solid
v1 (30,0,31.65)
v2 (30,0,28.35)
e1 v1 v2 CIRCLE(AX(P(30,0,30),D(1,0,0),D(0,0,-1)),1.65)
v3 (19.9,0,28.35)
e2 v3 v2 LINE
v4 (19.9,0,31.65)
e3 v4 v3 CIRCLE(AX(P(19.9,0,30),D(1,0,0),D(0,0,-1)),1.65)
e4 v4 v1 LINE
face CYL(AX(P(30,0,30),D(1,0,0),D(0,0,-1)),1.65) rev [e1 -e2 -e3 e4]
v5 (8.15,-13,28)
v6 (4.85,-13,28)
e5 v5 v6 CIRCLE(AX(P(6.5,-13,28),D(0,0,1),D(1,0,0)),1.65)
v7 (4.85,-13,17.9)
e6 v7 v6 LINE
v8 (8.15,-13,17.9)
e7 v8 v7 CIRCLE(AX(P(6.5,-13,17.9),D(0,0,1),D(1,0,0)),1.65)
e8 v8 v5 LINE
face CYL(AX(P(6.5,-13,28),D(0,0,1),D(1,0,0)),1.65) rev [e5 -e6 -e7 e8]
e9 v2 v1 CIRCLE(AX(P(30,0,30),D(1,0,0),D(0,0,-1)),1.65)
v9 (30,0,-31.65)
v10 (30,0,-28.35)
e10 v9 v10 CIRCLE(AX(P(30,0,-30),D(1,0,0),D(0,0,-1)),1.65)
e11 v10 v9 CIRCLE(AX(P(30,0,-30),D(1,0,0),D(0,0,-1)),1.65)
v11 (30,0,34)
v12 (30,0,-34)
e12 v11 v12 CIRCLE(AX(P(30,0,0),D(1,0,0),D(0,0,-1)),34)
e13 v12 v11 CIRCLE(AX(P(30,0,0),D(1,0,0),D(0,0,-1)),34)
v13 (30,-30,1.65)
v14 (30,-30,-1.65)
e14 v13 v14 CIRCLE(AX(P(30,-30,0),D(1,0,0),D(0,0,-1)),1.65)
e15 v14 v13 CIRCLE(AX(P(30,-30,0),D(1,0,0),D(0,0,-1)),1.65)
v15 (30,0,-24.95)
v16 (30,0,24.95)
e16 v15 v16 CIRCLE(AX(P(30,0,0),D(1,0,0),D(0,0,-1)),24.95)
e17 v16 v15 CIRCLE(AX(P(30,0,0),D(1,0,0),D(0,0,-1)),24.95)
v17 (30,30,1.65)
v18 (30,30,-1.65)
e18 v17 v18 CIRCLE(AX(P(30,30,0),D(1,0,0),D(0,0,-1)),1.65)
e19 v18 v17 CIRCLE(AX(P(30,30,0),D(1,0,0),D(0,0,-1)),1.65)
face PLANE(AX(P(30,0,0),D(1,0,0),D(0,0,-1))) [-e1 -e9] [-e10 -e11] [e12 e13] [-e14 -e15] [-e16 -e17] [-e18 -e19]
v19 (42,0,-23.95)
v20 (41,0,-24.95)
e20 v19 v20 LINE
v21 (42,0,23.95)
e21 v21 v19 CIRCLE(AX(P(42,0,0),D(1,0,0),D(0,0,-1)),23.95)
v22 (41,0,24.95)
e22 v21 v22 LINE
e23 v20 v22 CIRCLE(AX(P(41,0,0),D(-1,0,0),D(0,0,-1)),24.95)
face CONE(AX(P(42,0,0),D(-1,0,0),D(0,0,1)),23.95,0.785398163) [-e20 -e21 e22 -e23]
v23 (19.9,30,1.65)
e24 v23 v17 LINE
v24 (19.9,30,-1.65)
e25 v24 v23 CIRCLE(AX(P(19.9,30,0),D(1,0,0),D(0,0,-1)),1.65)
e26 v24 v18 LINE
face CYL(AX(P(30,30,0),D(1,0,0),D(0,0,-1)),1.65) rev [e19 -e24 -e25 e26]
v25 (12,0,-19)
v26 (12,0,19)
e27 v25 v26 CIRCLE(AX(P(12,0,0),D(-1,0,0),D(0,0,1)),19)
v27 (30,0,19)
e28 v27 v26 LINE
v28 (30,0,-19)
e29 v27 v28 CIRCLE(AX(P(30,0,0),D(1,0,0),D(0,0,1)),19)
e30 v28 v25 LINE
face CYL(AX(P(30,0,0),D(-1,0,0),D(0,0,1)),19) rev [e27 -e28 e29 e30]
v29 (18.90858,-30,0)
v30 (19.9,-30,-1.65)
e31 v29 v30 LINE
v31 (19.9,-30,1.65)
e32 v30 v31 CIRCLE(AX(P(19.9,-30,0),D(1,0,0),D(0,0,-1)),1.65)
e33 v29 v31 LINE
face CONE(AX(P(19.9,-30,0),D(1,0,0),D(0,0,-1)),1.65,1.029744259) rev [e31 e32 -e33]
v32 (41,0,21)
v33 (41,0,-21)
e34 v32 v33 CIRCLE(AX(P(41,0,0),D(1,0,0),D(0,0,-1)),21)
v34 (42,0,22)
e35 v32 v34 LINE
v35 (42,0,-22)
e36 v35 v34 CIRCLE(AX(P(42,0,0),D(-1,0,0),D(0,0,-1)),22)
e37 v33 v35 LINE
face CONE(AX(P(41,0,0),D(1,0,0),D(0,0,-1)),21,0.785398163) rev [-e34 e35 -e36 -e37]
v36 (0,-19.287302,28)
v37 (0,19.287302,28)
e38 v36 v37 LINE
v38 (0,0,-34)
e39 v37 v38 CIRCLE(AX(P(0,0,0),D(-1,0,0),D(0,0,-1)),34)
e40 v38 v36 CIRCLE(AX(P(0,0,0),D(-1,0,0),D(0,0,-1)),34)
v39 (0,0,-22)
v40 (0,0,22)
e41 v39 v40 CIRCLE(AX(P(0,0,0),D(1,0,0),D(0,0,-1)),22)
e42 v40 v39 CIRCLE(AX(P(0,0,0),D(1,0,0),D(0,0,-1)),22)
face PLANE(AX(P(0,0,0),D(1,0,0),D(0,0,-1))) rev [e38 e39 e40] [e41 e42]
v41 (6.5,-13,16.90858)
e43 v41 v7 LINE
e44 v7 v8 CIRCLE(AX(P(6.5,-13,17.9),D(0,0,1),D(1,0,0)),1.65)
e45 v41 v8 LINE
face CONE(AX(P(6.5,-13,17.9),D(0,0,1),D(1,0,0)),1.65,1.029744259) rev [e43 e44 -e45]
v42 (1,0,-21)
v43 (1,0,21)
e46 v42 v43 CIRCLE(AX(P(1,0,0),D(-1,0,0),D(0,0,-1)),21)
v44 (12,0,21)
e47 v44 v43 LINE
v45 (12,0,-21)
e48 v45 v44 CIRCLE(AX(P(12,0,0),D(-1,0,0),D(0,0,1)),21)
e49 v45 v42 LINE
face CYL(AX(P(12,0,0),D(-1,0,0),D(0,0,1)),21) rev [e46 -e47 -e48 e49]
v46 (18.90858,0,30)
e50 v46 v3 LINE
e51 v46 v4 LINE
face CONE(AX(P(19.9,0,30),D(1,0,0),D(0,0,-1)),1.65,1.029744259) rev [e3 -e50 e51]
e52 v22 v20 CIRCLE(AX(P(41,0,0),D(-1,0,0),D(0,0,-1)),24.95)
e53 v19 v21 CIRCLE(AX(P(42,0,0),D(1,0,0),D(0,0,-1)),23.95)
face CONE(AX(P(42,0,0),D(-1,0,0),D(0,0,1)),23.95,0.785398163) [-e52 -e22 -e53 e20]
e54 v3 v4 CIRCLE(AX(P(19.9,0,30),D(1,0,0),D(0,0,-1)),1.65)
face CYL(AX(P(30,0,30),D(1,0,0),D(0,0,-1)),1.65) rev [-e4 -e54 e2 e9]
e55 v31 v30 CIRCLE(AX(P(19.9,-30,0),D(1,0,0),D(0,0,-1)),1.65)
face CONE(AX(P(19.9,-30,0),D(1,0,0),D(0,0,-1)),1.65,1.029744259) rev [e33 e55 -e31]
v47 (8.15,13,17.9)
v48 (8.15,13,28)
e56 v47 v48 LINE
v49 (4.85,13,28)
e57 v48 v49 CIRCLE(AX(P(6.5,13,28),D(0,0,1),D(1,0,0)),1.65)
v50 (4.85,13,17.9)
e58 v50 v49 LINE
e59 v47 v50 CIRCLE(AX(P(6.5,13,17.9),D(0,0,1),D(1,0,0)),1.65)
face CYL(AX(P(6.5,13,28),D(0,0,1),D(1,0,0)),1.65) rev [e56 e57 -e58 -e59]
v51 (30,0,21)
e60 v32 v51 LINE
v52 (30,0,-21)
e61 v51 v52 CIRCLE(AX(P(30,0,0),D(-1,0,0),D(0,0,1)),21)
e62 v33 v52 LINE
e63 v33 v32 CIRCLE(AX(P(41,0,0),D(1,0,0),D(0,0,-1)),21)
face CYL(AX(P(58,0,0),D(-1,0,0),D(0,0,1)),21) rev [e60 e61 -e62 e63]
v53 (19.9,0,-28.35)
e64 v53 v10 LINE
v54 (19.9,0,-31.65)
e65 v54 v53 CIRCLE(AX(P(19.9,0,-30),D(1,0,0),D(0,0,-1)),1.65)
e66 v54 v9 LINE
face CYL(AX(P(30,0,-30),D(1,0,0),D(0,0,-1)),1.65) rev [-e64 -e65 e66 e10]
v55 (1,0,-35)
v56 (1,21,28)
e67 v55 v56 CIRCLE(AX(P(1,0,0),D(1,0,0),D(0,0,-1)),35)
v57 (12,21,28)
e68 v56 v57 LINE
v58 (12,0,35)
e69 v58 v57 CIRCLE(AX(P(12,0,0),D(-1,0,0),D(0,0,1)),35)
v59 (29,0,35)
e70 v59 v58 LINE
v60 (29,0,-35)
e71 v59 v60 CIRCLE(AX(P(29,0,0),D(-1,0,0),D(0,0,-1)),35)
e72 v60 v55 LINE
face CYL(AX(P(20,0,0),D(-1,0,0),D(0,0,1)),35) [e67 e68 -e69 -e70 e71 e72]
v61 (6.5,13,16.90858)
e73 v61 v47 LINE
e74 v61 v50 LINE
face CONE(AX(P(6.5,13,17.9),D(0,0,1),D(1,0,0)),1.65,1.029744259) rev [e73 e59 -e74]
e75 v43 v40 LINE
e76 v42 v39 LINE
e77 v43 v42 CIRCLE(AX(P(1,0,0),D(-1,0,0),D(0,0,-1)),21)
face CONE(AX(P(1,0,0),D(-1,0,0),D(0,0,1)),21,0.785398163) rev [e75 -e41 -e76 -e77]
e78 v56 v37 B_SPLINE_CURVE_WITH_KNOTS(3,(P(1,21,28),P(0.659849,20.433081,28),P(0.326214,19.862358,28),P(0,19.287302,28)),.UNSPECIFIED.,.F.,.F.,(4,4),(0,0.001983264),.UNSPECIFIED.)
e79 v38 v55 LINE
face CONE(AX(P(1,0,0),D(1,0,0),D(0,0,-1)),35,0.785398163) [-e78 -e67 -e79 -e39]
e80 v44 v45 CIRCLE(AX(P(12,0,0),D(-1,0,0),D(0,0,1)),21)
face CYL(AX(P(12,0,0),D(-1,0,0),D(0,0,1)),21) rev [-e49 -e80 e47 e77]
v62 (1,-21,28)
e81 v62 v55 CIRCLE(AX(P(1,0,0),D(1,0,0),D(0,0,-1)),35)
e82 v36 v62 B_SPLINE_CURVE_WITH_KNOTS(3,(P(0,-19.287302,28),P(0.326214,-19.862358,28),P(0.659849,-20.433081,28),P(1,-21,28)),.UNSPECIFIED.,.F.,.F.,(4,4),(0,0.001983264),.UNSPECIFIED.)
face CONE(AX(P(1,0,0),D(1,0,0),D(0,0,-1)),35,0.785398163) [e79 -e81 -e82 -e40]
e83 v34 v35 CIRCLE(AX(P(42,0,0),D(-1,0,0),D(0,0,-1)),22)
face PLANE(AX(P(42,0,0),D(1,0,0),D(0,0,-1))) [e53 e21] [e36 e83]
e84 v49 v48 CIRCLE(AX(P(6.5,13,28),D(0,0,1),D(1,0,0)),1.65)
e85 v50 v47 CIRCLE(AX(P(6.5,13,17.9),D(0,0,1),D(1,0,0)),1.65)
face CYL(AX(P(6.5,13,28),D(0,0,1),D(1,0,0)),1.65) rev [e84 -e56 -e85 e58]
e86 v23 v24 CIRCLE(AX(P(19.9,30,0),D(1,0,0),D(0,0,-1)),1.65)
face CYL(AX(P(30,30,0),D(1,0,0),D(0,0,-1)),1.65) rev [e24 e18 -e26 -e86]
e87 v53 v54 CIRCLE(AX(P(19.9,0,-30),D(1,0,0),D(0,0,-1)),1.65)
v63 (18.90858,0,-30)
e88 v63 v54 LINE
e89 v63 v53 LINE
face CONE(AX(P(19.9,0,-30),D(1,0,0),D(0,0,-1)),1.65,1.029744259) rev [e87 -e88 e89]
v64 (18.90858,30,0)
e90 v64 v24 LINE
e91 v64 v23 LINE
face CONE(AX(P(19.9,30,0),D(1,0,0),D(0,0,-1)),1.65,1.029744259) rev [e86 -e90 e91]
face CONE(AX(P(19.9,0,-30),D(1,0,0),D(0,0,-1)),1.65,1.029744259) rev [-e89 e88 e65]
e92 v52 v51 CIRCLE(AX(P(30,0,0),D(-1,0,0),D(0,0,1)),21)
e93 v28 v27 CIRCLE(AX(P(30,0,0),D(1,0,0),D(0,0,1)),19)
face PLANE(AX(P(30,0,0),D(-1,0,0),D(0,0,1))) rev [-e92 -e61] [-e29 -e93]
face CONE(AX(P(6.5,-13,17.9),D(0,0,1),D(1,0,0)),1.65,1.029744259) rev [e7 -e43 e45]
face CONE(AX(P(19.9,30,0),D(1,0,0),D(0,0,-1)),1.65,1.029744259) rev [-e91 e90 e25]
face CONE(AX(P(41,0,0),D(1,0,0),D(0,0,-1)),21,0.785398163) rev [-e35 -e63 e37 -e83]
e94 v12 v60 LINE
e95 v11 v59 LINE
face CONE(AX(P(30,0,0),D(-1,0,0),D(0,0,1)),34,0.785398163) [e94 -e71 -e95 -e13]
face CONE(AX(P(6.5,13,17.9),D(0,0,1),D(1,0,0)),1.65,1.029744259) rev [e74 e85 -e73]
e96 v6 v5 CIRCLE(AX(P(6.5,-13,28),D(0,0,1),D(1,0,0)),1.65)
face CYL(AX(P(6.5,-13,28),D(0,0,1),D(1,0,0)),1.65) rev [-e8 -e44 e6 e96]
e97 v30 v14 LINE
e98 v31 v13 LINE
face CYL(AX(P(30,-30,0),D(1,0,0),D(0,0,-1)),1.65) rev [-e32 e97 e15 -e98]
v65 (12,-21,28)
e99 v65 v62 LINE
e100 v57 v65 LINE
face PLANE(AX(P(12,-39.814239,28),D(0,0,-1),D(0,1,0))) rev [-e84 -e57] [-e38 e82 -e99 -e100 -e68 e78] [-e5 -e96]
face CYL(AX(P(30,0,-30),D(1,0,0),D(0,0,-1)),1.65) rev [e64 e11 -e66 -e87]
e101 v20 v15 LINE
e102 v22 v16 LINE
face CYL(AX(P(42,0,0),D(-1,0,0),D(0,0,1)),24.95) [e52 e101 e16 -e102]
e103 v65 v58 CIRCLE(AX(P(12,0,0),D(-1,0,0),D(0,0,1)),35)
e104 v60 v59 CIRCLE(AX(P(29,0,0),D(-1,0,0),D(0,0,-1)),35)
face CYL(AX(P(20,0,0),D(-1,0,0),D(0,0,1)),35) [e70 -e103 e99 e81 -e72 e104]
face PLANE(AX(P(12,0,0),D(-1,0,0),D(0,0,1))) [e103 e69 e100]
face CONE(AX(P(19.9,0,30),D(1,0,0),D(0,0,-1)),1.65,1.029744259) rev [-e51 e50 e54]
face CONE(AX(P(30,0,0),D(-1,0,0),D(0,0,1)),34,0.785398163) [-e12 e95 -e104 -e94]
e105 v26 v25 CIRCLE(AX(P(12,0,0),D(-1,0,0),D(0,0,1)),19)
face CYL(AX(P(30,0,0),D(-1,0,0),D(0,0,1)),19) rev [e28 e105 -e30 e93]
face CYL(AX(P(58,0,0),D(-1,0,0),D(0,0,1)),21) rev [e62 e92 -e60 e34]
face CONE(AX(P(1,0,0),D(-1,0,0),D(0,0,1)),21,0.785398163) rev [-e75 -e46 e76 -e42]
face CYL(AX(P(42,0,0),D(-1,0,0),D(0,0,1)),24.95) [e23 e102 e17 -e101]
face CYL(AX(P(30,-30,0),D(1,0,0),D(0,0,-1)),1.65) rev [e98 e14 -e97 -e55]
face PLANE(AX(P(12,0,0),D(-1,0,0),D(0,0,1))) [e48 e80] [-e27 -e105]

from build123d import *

# Parameters (mm, degrees)
SKETCH1_R             = 35
BOSS_EXTRUDE1_DEPTH   = 20
SKETCH2_R             = 35
BOSS_EXTRUDE2_DEPTH   = 10
SKETCH3_R             = 24.95
BOSS_EXTRUDE3_DEPTH   = 12
SKETCH4_R             = 21
CUT_EXTRUDE1_DEPTH    = 12
SKETCH5_R             = 19
CUT_EXTRUDE2_DEPTH    = 18
SKETCH6_R             = 21
CUT_EXTRUDE3_DEPTH    = 28
CIRPATTERN1_COUNT     = 4
SKETCH9_W             = 82.925750659
SKETCH9_H             = 79.628478102
CUT_EXTRUDE4_DEPTH    = 12
M4_TAPPED_HOLE3_D     = 3.3
M4_TAPPED_HOLE3_DEPTH = 10.1
M4_TAPPED_HOLE3_TIP   = 0.991420021
CHAMFER1_SIZE         = 1


with BuildPart() as part:
    # Sketch1 → Boss-Extrude1 (new body)
    with BuildSketch(Plane(origin=(0, 0, 0), x_dir=(0, 0, -1), z_dir=(1, 0, 0))):
        Circle(SKETCH1_R)
    extrude(amount=BOSS_EXTRUDE1_DEPTH)

    # Sketch2 → Boss-Extrude2 (add)
    with BuildSketch(Plane(origin=(20, 0, 0), x_dir=(0, 0, -1), z_dir=(1, 0, 0))):
        Circle(SKETCH2_R)
    extrude(amount=BOSS_EXTRUDE2_DEPTH)

    # Sketch3 → Boss-Extrude3 (add)
    with BuildSketch(Plane(origin=(30, 0, 0), x_dir=(0, 0, -1), z_dir=(1, 0, 0))):
        Circle(SKETCH3_R)
    extrude(amount=BOSS_EXTRUDE3_DEPTH)

    # Sketch4 → Cut-Extrude1 (cut)
    with BuildSketch(Plane.ZY):
        Circle(SKETCH4_R)
    extrude(amount=-CUT_EXTRUDE1_DEPTH, mode=Mode.SUBTRACT)

    # Sketch5 → Cut-Extrude2 (cut)
    with BuildSketch(Plane.ZY.offset(-12)):
        Circle(SKETCH5_R)
    extrude(amount=-CUT_EXTRUDE2_DEPTH, mode=Mode.SUBTRACT)

    # Sketch6 → Cut-Extrude3 (cut)
    with BuildSketch(Plane.ZY.offset(-30)):
        Circle(SKETCH6_R)
    extrude(amount=-CUT_EXTRUDE3_DEPTH, mode=Mode.SUBTRACT)

    # Sketch7 → M4 Tapped Hole2 (revolve, cut)
    with BuildSketch(Plane(origin=(30, 0, -30), x_dir=(0, 0, -1), z_dir=(0, 1, 0))):
        Polygon((0, 0), (0, 11.091420021), (1.65, 10.1), (1.65, 0), align=None)
    m4_tapped_hole2 = revolve(axis=Axis((36.35, 0, -30), (-1, 0, 0)), mode=Mode.SUBTRACT)

    # CirPattern1: M4 Tapped Hole2 ×4 about axis
    cirpattern1_axis = Axis((0, 0, 0), (1, 0, 0))
    for i in range(1, CIRPATTERN1_COUNT):
        add(m4_tapped_hole2.rotate(cirpattern1_axis, i * 360 / CIRPATTERN1_COUNT), mode=Mode.SUBTRACT)

    # Sketch9 → Cut-Extrude4 (cut)
    with BuildSketch(Plane.ZY):
        with Locations((69.46287533, 0)):
            Rectangle(SKETCH9_W, SKETCH9_H)
    extrude(amount=-CUT_EXTRUDE4_DEPTH, mode=Mode.SUBTRACT)

    # M4 Tapped Hole3
    with Locations(Plane.XY.offset(28)):
        with Locations((6.5, 13), (6.5, -13)):
            Hole(M4_TAPPED_HOLE3_D / 2, depth=M4_TAPPED_HOLE3_DEPTH)
            with Locations((0, 0, -(M4_TAPPED_HOLE3_DEPTH + M4_TAPPED_HOLE3_TIP / 2))):  # 118° drill point
                Cone(0, M4_TAPPED_HOLE3_D / 2, M4_TAPPED_HOLE3_TIP, mode=Mode.SUBTRACT)

    # Chamfer1
    chamfer1_edges = [part.edges().sort_by_distance(p)[0] for p in [
        (42, 0, 24.95),
        (0, 0, -21),
        (42, 0, -21),
        (0, 33.203915432, -11.067971811),
        (30, 0, 35),
    ]]
    chamfer(chamfer1_edges, length=CHAMFER1_SIZE)


solid = part.part
